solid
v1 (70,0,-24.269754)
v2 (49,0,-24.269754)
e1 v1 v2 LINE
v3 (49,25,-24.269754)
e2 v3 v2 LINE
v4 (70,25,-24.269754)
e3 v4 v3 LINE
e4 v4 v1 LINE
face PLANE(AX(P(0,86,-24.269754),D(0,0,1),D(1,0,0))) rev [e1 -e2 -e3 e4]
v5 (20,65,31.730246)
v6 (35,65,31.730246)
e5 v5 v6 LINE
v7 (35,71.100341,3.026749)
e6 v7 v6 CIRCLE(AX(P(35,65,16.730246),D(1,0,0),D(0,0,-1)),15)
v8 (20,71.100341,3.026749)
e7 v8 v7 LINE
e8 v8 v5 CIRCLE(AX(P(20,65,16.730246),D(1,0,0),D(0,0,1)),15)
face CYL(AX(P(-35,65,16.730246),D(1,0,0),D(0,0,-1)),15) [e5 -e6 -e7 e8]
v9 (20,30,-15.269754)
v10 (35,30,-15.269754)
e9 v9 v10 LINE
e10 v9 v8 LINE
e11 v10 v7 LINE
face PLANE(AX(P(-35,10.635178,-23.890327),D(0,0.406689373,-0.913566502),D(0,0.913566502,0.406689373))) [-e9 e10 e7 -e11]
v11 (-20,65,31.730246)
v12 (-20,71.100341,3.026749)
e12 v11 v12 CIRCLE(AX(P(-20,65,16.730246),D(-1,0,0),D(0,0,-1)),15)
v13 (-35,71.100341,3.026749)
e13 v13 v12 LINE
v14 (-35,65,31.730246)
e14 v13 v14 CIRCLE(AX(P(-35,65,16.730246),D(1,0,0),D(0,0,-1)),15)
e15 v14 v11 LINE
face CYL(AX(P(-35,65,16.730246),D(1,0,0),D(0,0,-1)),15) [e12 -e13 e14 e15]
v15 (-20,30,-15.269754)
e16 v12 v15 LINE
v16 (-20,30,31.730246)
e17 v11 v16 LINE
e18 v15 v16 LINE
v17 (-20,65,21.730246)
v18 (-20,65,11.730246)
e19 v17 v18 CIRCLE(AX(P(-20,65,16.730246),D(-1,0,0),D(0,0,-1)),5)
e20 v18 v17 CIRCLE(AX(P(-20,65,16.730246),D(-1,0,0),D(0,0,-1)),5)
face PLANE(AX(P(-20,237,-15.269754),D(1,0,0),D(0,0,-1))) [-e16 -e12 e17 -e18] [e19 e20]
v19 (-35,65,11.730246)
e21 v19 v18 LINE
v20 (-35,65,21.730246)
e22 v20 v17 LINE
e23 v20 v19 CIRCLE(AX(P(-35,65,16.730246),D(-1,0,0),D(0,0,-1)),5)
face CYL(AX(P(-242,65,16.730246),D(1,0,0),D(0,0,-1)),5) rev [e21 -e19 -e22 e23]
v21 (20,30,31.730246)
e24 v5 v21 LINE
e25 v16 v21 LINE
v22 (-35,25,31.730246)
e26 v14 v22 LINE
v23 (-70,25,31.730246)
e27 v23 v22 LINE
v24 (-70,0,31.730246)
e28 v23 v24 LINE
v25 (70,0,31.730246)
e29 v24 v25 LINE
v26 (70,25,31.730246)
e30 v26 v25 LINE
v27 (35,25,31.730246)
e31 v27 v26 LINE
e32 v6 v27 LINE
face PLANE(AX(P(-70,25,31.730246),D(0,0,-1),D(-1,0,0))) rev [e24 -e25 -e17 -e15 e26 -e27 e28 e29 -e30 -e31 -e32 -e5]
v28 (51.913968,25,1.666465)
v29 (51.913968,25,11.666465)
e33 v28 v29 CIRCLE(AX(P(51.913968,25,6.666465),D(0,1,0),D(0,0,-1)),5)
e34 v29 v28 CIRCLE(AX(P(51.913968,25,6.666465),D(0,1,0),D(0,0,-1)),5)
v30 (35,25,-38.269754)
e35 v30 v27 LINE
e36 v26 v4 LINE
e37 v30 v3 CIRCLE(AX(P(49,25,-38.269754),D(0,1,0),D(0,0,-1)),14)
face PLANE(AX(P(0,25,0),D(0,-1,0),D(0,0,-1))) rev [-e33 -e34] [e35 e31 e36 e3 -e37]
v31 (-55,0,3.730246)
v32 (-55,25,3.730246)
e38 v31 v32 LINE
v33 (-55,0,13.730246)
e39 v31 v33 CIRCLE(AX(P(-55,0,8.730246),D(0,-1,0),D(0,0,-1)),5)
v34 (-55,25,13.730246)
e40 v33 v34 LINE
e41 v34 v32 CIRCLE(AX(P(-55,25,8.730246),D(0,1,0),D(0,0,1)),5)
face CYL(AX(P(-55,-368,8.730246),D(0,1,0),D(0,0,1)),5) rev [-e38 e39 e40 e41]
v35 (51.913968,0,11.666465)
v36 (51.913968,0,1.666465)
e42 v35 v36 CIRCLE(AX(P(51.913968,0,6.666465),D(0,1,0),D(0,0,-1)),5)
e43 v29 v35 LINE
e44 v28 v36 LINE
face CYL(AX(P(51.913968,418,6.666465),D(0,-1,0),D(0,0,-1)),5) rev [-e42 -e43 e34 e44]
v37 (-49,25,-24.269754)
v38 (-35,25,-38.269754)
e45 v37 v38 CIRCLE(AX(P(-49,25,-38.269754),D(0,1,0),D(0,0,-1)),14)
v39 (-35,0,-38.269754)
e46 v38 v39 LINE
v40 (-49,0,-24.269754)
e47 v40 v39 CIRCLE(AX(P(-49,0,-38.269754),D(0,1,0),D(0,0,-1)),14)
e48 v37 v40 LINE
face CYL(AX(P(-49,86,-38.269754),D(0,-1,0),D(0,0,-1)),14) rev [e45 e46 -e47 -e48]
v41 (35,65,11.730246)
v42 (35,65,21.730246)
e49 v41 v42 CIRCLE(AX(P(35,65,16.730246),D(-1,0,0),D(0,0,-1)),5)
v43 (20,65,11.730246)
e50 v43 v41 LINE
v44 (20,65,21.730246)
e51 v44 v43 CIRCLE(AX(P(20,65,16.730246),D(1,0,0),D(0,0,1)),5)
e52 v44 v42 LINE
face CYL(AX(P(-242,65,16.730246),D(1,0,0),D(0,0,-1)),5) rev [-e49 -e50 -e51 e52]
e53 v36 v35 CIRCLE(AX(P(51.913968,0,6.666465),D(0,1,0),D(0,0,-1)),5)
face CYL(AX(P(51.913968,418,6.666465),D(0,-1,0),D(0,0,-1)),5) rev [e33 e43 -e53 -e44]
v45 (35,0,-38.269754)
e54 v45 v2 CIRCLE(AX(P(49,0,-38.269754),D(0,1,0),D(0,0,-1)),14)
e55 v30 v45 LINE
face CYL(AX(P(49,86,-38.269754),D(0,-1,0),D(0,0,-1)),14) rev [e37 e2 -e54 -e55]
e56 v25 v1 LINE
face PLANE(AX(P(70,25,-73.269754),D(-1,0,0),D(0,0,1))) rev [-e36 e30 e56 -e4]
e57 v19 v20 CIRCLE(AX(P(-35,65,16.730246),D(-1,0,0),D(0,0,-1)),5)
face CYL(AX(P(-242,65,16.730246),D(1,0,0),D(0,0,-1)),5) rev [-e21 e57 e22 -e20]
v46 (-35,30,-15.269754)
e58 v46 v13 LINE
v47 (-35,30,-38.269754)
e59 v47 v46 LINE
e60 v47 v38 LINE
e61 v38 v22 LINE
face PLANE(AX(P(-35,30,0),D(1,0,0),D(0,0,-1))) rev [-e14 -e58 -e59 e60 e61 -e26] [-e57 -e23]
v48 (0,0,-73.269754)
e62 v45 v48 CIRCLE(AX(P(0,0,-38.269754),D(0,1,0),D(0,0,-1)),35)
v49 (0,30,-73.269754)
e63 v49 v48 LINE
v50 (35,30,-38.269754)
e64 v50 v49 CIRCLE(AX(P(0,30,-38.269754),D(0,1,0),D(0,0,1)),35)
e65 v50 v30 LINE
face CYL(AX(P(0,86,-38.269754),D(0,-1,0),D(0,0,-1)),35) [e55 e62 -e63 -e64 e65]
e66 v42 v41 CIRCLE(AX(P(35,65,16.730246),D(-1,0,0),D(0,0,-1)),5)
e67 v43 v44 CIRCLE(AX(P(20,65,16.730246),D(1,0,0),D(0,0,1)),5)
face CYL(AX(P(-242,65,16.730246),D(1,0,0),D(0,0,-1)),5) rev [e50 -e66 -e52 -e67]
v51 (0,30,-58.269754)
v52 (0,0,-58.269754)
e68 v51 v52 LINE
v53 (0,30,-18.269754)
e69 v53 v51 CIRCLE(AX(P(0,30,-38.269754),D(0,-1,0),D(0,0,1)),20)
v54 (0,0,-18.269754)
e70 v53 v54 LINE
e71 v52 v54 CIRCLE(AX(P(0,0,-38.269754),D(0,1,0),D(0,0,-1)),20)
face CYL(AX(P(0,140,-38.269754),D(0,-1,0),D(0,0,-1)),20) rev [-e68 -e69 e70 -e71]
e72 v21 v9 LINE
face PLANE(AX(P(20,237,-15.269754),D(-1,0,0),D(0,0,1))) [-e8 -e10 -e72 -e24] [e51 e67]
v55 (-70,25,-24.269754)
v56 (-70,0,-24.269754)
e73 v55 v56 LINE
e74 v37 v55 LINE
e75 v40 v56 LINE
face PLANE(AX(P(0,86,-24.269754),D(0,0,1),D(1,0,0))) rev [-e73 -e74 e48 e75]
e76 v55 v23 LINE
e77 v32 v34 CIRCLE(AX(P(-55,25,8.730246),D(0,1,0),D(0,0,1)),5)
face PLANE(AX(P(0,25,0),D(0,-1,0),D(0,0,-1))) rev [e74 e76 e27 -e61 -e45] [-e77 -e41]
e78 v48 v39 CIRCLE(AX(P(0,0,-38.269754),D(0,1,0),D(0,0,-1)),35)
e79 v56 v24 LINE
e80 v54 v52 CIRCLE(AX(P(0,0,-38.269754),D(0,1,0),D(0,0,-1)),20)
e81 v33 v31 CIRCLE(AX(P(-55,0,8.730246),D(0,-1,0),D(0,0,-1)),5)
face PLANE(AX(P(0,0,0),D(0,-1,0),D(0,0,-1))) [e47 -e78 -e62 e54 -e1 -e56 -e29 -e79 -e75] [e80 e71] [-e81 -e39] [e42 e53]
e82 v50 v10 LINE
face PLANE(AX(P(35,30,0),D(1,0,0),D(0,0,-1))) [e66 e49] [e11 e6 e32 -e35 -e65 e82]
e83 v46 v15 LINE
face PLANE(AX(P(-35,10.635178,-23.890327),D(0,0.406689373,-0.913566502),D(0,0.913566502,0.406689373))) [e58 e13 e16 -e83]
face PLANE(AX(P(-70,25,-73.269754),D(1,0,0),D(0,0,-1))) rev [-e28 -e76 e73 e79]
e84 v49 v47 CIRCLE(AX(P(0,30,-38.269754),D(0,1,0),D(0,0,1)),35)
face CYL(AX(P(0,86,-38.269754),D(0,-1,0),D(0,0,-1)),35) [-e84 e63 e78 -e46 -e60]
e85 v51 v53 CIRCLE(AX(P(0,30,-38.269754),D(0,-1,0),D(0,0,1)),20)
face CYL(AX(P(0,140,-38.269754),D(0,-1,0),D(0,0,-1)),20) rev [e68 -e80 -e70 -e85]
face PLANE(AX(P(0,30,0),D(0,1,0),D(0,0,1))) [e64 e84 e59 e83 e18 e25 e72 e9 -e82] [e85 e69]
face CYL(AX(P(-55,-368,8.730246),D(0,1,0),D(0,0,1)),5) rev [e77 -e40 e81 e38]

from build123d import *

# Parameters (mm, degrees)
BASE_PLATE_DEPTH               = 25
HOUSING_PROFILE_CUT_DEPTH      = 61
HOUSING_PROFILE_CUT_DEPTH_BACK = 91
HOUSING_BOSS_DEPTH             = 5
BORE_40_DEPTH                  = 110
BORE_40_DEPTH_BACK             = 116
BORE_40_SKETCH_R               = 20
MOUNTING_HOLE_10_A_SKETCH_R    = 5
MOUNTING_HOLE_10_A_DEPTH       = 393
MOUNTING_HOLE_10_B_DEPTH       = 393
MOUNTING_HOLE_10_B_DEPTH_BACK  = 393
MOUNTING_HOLE_10_B_SKETCH_R    = 5
CLEVIS_LUGS_DEPTH              = 70
LUG_GAP_CUT_SKETCH_W           = 40
LUG_GAP_CUT_SKETCH_H           = 47
LUG_GAP_CUT_DEPTH              = 207
PIN_HOLE_10_DEPTH              = 207
PIN_HOLE_10_DEPTH_BACK         = 207
PIN_HOLE_10_SKETCH_R           = 5


with BuildPart() as part:
    # Base Plate Sketch → Base Plate (new body)
    with BuildSketch(Plane(origin=(0, 0, 0), x_dir=(1, 0, 0), z_dir=(0, 1, 0))):
        Polygon((-70, 95.100325632), (70, 95.100325632), (70, 73.269753582), (70, -31.730246418), (-70, -31.730246418), (-70, 73.269753582), align=None)
    extrude(amount=BASE_PLATE_DEPTH)

    # Housing Profile Cut Sketch → Housing Profile Cut (cut, two sides: drawn at the far end of the back side and taken through both)
    with BuildSketch(Plane(origin=(0, 25, 0), x_dir=(1, 0, 0), z_dir=(0, 1, 0)).offset(-HOUSING_PROFILE_CUT_DEPTH_BACK)):
        with BuildLine():
            Line((49, 24.269753582), (70, 24.269753582))
            Line((70, 24.269753582), (70, 95.100325632))
            Line((70, 95.100325632), (-70, 95.100325632))
            Line((-70, 95.100325632), (-70, 24.269753582))
            Line((-70, 24.269753582), (-49, 24.269753582))
            ThreePointArc((-49, 24.269753582), (-39.100505063, 28.370258646), (-35, 38.269753582))
            ThreePointArc((-35, 38.269753582), (0, 73.269753582), (35, 38.269753582))
            ThreePointArc((35, 38.269753582), (39.100505063, 28.370258646), (49, 24.269753582))
        make_face()
    extrude(amount=HOUSING_PROFILE_CUT_DEPTH + HOUSING_PROFILE_CUT_DEPTH_BACK, mode=Mode.SUBTRACT)

    # Housing Boss Sketch → Housing Boss (add)
    with BuildSketch(Plane(origin=(0, 25, 0), x_dir=(1, 0, 0), z_dir=(0, 1, 0))):
        with BuildLine():
            ThreePointArc((-35, 38.269753582), (0, 3.269753582), (35, 38.269753582))
            ThreePointArc((35, 38.269753582), (0, 73.269753582), (-35, 38.269753582))
        make_face()
        with BuildLine():
            Line((35, -31.730246418), (35, 38.269753582))
            ThreePointArc((35, 38.269753582), (0, 3.269753582), (-35, 38.269753582))
            Line((-35, 38.269753582), (-35, -31.730246418))
            Line((-35, -31.730246418), (35, -31.730246418))
        make_face()
    extrude(amount=HOUSING_BOSS_DEPTH)

    # Bore Ø40 Sketch → Bore Ø40 (cut, two sides: drawn at the far end of the back side and taken through both)
    with BuildSketch(Plane(origin=(0, 30, 0), x_dir=(1, 0, 0), z_dir=(0, 1, 0)).offset(-BORE_40_DEPTH_BACK)):
        with Locations(Location((0, 38.269753582, 0), (0, 0, 90))):
            Circle(BORE_40_SKETCH_R)
    extrude(amount=BORE_40_DEPTH + BORE_40_DEPTH_BACK, mode=Mode.SUBTRACT)

    # Mounting Hole Ø10 A Sketch → Mounting Hole Ø10 A (cut)
    with BuildSketch(Plane(origin=(0, 25, 0), x_dir=(1, 0, 0), z_dir=(0, 1, 0))):
        with Locations(Location((-55, -8.730246418, 0), (0, 0, 270))):
            Circle(MOUNTING_HOLE_10_A_SKETCH_R)
    extrude(amount=-MOUNTING_HOLE_10_A_DEPTH, mode=Mode.SUBTRACT)

    # Mounting Hole Ø10 B Sketch → Mounting Hole Ø10 B (cut, two sides: drawn at the far end of the back side and taken through both)
    with BuildSketch(Plane(origin=(0, 25, 0), x_dir=(1, 0, 0), z_dir=(0, 1, 0)).offset(-MOUNTING_HOLE_10_B_DEPTH_BACK)):
        with Locations(Location((51.913967656, -6.666465324, 0), (0, 0, 90))):
            Circle(MOUNTING_HOLE_10_B_SKETCH_R)
    extrude(amount=MOUNTING_HOLE_10_B_DEPTH + MOUNTING_HOLE_10_B_DEPTH_BACK, mode=Mode.SUBTRACT)

    # Clevis Lugs Sketch → Clevis Lugs (add)
    with BuildSketch(Plane(origin=(35, 0, 0), x_dir=(0, 0, -1), z_dir=(1, 0, 0))):
        with BuildLine():
            Line((-31.730246418, 65), (-31.730246418, 30))
            Line((-31.730246418, 30), (15.269753582, 30))
            Line((15.269753582, 30), (-3.026748887, 71.100340599))
            ThreePointArc((-3.026748887, 71.100340599), (-19.84854219, 79.67229469), (-31.730246418, 65))
        make_face()
    extrude(amount=-CLEVIS_LUGS_DEPTH)

    # Lug Gap Cut Sketch → Lug Gap Cut (cut)
    with BuildSketch(Plane(origin=(0, 30, 0), x_dir=(1, 0, 0), z_dir=(0, 1, 0))):
        with Locations((0, -8.230246418)):
            Rectangle(LUG_GAP_CUT_SKETCH_W, LUG_GAP_CUT_SKETCH_H)
    extrude(amount=LUG_GAP_CUT_DEPTH, mode=Mode.SUBTRACT)

    # Pin Hole Ø10 Sketch → Pin Hole Ø10 (cut, two sides: drawn at the far end of the back side and taken through both)
    with BuildSketch(Plane.ZY.offset(35).offset(-PIN_HOLE_10_DEPTH_BACK)):
        with Locations(Location((16.730246418, 65, 0), (0, 0, 180))):
            Circle(PIN_HOLE_10_SKETCH_R)
    extrude(amount=PIN_HOLE_10_DEPTH + PIN_HOLE_10_DEPTH_BACK, mode=Mode.SUBTRACT)


solid = part.part
